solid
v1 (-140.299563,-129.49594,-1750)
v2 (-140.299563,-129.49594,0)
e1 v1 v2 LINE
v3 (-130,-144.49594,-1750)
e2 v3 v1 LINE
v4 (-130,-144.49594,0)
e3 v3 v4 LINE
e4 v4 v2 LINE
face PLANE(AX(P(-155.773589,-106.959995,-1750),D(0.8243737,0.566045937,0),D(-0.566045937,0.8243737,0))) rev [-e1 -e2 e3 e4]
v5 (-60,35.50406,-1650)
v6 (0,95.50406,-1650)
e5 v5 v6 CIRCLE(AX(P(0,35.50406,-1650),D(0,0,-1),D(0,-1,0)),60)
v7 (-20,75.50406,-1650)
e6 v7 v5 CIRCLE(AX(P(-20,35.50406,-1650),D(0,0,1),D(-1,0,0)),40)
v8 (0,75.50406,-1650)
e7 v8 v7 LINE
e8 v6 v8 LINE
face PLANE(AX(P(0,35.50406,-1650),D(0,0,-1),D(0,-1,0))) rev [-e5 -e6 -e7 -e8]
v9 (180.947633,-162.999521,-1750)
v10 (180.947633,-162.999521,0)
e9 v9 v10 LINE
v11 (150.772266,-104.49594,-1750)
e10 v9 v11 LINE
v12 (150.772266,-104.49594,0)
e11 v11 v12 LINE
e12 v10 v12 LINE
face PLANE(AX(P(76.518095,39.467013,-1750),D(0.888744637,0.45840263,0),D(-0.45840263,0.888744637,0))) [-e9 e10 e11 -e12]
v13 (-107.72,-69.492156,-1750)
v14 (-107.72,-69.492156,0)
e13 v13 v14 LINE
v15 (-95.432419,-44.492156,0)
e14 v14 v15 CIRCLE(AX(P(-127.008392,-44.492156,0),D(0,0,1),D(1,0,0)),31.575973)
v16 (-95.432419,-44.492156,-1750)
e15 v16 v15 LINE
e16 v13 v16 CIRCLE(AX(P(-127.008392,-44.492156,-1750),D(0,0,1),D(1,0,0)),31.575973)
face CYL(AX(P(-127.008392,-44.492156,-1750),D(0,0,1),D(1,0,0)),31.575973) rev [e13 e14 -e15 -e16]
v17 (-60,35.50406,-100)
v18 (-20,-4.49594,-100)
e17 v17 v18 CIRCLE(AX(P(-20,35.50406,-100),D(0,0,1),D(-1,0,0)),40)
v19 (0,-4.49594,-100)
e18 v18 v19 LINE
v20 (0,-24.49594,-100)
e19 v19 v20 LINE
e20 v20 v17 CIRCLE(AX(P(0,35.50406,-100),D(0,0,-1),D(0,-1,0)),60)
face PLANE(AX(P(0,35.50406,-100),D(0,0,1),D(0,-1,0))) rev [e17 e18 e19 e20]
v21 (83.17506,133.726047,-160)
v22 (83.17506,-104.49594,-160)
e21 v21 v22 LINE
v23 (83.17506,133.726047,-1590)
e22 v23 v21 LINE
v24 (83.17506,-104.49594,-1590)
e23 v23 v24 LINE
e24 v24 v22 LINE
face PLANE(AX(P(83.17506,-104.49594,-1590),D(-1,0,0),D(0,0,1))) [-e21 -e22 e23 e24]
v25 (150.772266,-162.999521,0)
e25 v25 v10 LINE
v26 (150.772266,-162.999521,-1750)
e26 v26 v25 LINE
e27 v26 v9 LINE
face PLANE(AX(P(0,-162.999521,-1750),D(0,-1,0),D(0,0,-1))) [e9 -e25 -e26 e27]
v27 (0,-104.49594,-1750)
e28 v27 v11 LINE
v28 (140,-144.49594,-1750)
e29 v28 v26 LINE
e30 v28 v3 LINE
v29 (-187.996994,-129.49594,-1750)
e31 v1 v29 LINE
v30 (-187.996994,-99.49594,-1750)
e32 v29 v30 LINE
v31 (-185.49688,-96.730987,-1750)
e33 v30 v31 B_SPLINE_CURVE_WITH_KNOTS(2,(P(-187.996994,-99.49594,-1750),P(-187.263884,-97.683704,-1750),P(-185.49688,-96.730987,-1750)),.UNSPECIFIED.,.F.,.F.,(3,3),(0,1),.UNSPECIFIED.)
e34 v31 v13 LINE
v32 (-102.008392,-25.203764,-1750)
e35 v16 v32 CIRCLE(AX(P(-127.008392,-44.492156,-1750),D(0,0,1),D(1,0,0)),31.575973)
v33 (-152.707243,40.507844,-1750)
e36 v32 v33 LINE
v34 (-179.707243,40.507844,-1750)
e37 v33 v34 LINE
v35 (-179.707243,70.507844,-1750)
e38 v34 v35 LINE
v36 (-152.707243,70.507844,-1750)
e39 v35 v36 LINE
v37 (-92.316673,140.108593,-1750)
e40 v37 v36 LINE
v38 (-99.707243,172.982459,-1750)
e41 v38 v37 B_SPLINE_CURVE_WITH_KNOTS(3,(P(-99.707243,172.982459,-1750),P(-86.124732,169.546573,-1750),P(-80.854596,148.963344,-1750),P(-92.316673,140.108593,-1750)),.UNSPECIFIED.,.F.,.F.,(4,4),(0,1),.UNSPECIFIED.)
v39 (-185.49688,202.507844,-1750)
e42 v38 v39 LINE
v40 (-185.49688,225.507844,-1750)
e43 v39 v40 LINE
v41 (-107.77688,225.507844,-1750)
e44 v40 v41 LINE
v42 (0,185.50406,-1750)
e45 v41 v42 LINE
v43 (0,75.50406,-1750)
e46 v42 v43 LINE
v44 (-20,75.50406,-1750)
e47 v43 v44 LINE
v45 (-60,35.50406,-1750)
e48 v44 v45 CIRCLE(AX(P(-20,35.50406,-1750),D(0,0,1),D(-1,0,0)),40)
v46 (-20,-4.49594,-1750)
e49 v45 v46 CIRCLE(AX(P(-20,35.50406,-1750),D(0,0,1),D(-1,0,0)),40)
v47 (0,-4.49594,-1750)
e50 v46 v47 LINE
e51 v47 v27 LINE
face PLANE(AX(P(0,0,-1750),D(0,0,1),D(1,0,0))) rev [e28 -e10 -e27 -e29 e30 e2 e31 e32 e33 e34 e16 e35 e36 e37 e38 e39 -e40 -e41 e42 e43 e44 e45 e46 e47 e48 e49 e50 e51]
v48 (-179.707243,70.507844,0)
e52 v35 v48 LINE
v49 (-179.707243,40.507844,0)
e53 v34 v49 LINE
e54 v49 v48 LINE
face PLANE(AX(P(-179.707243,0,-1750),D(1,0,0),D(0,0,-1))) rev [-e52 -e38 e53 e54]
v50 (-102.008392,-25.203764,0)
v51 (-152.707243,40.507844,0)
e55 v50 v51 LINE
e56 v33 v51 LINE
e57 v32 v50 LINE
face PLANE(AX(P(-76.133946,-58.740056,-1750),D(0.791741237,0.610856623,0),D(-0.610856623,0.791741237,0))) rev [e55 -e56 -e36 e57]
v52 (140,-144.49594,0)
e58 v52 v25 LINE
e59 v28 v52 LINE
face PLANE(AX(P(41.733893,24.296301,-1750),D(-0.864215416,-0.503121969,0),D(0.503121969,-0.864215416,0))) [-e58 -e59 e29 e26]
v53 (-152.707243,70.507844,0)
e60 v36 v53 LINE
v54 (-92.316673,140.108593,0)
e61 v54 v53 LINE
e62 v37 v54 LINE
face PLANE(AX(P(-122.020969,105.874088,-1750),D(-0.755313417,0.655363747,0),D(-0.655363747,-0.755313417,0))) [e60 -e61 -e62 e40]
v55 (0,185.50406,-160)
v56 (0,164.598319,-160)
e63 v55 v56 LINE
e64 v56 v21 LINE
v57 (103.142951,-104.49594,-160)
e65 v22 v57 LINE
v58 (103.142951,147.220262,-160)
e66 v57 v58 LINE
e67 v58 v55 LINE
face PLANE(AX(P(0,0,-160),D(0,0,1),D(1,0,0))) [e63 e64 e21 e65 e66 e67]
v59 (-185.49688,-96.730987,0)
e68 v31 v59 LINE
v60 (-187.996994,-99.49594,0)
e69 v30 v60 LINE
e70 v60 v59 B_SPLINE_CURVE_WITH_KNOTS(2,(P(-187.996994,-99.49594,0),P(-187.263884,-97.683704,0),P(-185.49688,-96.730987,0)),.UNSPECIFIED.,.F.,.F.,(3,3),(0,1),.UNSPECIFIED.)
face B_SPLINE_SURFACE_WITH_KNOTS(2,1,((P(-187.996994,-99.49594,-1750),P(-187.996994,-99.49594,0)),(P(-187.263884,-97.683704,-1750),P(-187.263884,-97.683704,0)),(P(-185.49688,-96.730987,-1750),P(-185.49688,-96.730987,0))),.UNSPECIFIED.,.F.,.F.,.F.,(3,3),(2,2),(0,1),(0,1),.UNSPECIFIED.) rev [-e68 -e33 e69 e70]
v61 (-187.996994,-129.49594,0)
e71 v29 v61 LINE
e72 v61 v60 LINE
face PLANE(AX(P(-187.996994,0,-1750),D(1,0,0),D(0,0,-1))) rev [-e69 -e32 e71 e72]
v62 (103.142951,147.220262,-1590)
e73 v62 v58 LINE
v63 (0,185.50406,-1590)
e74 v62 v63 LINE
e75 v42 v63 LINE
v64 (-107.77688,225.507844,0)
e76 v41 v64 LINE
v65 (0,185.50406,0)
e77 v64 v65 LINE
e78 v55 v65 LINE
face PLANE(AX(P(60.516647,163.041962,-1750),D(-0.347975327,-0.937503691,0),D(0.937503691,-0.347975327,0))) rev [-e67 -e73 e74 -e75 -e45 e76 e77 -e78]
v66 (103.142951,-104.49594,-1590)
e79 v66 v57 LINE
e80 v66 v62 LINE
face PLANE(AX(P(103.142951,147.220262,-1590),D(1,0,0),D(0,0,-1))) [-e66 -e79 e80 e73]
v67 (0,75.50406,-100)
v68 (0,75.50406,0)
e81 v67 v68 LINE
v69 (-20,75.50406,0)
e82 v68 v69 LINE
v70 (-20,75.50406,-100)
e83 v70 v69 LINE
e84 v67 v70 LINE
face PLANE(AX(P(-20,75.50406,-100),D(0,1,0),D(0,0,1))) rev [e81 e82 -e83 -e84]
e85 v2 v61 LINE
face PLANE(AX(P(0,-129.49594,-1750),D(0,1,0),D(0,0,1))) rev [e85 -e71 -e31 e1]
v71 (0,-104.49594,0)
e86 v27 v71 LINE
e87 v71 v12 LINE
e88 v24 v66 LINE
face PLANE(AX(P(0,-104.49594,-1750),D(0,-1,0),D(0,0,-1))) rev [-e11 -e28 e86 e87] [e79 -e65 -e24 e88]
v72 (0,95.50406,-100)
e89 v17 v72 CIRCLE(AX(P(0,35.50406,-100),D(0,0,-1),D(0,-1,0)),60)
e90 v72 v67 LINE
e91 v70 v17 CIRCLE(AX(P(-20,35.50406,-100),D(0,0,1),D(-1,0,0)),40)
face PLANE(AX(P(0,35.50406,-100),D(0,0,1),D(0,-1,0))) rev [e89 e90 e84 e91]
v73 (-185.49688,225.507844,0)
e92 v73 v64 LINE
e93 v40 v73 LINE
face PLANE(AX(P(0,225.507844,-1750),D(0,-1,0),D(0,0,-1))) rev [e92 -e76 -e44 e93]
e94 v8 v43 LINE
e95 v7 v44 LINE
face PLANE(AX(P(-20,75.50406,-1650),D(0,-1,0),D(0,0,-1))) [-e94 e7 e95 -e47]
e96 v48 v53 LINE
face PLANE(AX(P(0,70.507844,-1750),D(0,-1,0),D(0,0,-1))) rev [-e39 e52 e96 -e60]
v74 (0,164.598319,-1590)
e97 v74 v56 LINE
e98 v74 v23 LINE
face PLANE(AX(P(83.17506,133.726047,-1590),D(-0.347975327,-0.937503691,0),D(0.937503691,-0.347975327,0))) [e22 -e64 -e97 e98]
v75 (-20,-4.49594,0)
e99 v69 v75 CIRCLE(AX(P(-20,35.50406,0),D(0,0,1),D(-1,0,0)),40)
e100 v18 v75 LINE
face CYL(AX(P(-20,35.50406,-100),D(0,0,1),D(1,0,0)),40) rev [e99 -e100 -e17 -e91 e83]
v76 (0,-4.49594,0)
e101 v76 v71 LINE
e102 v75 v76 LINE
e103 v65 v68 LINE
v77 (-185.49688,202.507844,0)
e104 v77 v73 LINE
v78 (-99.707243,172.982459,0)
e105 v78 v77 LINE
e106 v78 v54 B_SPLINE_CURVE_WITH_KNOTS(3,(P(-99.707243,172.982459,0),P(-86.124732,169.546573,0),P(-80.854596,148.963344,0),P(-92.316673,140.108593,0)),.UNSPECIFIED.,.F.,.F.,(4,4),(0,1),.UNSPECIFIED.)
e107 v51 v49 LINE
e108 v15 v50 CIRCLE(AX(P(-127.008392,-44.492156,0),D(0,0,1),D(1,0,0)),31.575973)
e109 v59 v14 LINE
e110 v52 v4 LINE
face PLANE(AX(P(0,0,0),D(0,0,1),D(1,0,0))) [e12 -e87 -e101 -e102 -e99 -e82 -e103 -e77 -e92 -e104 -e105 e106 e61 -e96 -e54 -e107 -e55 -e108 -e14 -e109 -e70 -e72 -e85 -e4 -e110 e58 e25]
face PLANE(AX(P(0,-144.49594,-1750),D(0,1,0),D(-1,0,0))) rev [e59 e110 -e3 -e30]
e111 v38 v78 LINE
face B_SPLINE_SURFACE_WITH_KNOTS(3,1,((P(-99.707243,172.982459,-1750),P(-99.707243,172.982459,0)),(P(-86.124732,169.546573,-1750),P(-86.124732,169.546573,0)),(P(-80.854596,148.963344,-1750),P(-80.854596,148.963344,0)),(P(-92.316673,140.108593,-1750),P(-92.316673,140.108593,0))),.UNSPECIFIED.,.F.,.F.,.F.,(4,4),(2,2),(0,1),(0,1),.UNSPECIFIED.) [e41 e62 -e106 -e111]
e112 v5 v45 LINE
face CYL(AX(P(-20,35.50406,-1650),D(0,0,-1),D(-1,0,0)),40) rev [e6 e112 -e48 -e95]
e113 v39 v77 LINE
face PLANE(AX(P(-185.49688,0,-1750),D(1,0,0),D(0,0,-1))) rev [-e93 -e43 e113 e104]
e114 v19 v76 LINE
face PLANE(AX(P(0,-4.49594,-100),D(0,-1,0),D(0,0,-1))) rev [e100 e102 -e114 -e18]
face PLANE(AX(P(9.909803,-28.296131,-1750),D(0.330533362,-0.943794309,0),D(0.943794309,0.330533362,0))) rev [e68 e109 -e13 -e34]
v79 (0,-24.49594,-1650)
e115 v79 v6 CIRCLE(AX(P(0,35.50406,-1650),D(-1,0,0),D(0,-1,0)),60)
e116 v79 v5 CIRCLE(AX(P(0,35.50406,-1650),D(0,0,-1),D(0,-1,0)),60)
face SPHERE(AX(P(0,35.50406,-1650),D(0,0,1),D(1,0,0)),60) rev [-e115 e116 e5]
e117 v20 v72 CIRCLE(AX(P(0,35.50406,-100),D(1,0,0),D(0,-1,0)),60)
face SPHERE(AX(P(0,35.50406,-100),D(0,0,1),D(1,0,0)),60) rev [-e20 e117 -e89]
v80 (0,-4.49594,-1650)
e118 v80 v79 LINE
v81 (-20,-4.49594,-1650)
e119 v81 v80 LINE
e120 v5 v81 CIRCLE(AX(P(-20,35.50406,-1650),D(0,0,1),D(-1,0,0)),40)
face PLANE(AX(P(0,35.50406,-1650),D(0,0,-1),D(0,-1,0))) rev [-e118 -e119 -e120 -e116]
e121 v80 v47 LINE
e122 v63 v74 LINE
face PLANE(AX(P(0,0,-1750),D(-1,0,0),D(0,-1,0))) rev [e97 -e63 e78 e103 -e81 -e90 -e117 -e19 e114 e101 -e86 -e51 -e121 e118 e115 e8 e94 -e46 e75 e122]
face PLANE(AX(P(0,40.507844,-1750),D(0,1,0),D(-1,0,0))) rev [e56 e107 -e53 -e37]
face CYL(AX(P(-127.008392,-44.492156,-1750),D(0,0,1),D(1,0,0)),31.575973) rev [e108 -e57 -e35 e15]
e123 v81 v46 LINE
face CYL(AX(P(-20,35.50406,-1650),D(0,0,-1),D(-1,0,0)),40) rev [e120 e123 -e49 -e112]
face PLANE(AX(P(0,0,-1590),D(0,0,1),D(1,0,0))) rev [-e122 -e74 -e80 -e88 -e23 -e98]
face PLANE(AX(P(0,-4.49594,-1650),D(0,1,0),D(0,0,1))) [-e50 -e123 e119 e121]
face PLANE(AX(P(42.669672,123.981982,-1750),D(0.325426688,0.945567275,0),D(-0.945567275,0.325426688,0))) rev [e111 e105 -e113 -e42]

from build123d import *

# Parameters (mm, degrees)
EXTRUDE_1_DEPTH     = 1750
CUT_EXTRUDE_2_DEPTH = 100
CUT_REVOLVE_1_ANGLE = 90
EXTRUDE_2_DEPTH     = 1430


with BuildPart() as part:
    # 草图1 → 凸台-拉伸1 (new body)
    with BuildSketch(Plane.XY):
        with BuildLine():
            Line((-130, -144.49593989), (0, -144.49593989))
            Line((0, -144.49593989), (140, -144.49593989))
            Line((140, -144.49593989), (150.772266034, -162.999521413))
            Line((150.772266034, -162.999521413), (180.947633082, -162.999521413))
            Line((180.947633082, -162.999521413), (150.772266034, -104.49593989))
            Line((150.772266034, -104.49593989), (0, -104.49593989))
            Line((0, -104.49593989), (0, -4.49593989))
            Line((0, -4.49593989), (0, 75.50406011))
            Line((0, 75.50406011), (0, 185.50406011))
            Line((0, 185.50406011), (-107.776879674, 225.507843927))
            Line((-107.776879674, 225.507843927), (-185.49687967, 225.507843927))
            Line((-185.49687967, 225.507843927), (-185.49687967, 202.507843927))
            Line((-185.49687967, 202.507843927), (-99.70724302, 172.98245945))
            add(Edge.make_bspline(
                [(-99.70724302, 172.98245945), (-86.12473236, 169.546572985), (-80.854596401, 148.963344023), (-92.316673431, 140.10859264)],
                knots=[0, 0, 0, 0, 1, 1, 1, 1], degree=3))
            Line((-92.316673431, 140.10859264), (-152.70724302, 70.507843927))
            Line((-152.70724302, 70.507843927), (-179.70724302, 70.507843927))
            Line((-179.70724302, 70.507843927), (-179.70724302, 40.507843927))
            Line((-179.70724302, 40.507843927), (-152.70724302, 40.507843927))
            Line((-152.70724302, 40.507843927), (-102.0083923, -25.203763773))
            ThreePointArc((-102.0083923, -25.203763773), (-95.691769777, -48.530872609), (-107.72, -69.492156073))
            Line((-107.72, -69.492156073), (-185.49687967, -96.73098688))
            add(Edge.make_bspline(
                [(-187.99699364, -99.49593989), (-187.263883629, -97.683704139), (-185.49687967, -96.73098688)],
                knots=[0, 0, 0, 1, 1, 1], degree=2))
            Line((-187.99699364, -99.49593989), (-187.99699364, -129.49593989))
            Line((-187.99699364, -129.49593989), (-140.29956323, -129.49593989))
            Line((-140.29956323, -129.49593989), (-130, -144.49593989))
        make_face()
    extrude(amount=-EXTRUDE_1_DEPTH)

    # 草图2 → 切除-拉伸2 (cut)
    with BuildSketch(Plane.XY):
        with BuildLine():
            Line((0, 75.50406011), (0, -4.49593989))
            Line((0, -4.49593989), (-20, -4.49593989))
            ThreePointArc((-20, -4.49593989), (-60, 35.50406011), (-20, 75.50406011))
            Line((-20, 75.50406011), (0, 75.50406011))
        make_face()
    cut_extrude_2 = extrude(amount=-CUT_EXTRUDE_2_DEPTH, mode=Mode.SUBTRACT)

    # 草图4 → 切除-旋转1 (revolve, cut)
    with BuildSketch(Plane(origin=(0, 0, 0), x_dir=(0, 0, -1), z_dir=(1, 0, 0))):
        with BuildLine():
            Line((100, 95.50406011), (100, -24.49593989))
            ThreePointArc((100, -24.49593989), (160, 35.50406011), (100, 95.50406011))
        make_face()
    cut_revolve_1 = revolve(axis=Axis((0, 95.50406011, -100), (0, 1, 0)), revolution_arc=CUT_REVOLVE_1_ANGLE, mode=Mode.SUBTRACT)

    # 镜向1: 切除-拉伸2, 切除-旋转1 across plane
    add(cut_extrude_2.mirror(Plane.XY.offset(-875)), mode=Mode.SUBTRACT)
    add(cut_revolve_1.mirror(Plane.XY.offset(-875)), mode=Mode.SUBTRACT)

    # 草图6 → 凸台-拉伸2 (add)
    with BuildSketch(Plane.XY.offset(-160)):
        Polygon((0, 185.50406011), (63.207169624, 162.043314569), (103.142950665, 147.220262017), (103.142950665, -104.49593989), (83.175060144, -104.49593989), (83.175060144, 133.726046688), (0, 164.598318505), align=None)
    extrude(amount=-EXTRUDE_2_DEPTH)


solid = part.part
